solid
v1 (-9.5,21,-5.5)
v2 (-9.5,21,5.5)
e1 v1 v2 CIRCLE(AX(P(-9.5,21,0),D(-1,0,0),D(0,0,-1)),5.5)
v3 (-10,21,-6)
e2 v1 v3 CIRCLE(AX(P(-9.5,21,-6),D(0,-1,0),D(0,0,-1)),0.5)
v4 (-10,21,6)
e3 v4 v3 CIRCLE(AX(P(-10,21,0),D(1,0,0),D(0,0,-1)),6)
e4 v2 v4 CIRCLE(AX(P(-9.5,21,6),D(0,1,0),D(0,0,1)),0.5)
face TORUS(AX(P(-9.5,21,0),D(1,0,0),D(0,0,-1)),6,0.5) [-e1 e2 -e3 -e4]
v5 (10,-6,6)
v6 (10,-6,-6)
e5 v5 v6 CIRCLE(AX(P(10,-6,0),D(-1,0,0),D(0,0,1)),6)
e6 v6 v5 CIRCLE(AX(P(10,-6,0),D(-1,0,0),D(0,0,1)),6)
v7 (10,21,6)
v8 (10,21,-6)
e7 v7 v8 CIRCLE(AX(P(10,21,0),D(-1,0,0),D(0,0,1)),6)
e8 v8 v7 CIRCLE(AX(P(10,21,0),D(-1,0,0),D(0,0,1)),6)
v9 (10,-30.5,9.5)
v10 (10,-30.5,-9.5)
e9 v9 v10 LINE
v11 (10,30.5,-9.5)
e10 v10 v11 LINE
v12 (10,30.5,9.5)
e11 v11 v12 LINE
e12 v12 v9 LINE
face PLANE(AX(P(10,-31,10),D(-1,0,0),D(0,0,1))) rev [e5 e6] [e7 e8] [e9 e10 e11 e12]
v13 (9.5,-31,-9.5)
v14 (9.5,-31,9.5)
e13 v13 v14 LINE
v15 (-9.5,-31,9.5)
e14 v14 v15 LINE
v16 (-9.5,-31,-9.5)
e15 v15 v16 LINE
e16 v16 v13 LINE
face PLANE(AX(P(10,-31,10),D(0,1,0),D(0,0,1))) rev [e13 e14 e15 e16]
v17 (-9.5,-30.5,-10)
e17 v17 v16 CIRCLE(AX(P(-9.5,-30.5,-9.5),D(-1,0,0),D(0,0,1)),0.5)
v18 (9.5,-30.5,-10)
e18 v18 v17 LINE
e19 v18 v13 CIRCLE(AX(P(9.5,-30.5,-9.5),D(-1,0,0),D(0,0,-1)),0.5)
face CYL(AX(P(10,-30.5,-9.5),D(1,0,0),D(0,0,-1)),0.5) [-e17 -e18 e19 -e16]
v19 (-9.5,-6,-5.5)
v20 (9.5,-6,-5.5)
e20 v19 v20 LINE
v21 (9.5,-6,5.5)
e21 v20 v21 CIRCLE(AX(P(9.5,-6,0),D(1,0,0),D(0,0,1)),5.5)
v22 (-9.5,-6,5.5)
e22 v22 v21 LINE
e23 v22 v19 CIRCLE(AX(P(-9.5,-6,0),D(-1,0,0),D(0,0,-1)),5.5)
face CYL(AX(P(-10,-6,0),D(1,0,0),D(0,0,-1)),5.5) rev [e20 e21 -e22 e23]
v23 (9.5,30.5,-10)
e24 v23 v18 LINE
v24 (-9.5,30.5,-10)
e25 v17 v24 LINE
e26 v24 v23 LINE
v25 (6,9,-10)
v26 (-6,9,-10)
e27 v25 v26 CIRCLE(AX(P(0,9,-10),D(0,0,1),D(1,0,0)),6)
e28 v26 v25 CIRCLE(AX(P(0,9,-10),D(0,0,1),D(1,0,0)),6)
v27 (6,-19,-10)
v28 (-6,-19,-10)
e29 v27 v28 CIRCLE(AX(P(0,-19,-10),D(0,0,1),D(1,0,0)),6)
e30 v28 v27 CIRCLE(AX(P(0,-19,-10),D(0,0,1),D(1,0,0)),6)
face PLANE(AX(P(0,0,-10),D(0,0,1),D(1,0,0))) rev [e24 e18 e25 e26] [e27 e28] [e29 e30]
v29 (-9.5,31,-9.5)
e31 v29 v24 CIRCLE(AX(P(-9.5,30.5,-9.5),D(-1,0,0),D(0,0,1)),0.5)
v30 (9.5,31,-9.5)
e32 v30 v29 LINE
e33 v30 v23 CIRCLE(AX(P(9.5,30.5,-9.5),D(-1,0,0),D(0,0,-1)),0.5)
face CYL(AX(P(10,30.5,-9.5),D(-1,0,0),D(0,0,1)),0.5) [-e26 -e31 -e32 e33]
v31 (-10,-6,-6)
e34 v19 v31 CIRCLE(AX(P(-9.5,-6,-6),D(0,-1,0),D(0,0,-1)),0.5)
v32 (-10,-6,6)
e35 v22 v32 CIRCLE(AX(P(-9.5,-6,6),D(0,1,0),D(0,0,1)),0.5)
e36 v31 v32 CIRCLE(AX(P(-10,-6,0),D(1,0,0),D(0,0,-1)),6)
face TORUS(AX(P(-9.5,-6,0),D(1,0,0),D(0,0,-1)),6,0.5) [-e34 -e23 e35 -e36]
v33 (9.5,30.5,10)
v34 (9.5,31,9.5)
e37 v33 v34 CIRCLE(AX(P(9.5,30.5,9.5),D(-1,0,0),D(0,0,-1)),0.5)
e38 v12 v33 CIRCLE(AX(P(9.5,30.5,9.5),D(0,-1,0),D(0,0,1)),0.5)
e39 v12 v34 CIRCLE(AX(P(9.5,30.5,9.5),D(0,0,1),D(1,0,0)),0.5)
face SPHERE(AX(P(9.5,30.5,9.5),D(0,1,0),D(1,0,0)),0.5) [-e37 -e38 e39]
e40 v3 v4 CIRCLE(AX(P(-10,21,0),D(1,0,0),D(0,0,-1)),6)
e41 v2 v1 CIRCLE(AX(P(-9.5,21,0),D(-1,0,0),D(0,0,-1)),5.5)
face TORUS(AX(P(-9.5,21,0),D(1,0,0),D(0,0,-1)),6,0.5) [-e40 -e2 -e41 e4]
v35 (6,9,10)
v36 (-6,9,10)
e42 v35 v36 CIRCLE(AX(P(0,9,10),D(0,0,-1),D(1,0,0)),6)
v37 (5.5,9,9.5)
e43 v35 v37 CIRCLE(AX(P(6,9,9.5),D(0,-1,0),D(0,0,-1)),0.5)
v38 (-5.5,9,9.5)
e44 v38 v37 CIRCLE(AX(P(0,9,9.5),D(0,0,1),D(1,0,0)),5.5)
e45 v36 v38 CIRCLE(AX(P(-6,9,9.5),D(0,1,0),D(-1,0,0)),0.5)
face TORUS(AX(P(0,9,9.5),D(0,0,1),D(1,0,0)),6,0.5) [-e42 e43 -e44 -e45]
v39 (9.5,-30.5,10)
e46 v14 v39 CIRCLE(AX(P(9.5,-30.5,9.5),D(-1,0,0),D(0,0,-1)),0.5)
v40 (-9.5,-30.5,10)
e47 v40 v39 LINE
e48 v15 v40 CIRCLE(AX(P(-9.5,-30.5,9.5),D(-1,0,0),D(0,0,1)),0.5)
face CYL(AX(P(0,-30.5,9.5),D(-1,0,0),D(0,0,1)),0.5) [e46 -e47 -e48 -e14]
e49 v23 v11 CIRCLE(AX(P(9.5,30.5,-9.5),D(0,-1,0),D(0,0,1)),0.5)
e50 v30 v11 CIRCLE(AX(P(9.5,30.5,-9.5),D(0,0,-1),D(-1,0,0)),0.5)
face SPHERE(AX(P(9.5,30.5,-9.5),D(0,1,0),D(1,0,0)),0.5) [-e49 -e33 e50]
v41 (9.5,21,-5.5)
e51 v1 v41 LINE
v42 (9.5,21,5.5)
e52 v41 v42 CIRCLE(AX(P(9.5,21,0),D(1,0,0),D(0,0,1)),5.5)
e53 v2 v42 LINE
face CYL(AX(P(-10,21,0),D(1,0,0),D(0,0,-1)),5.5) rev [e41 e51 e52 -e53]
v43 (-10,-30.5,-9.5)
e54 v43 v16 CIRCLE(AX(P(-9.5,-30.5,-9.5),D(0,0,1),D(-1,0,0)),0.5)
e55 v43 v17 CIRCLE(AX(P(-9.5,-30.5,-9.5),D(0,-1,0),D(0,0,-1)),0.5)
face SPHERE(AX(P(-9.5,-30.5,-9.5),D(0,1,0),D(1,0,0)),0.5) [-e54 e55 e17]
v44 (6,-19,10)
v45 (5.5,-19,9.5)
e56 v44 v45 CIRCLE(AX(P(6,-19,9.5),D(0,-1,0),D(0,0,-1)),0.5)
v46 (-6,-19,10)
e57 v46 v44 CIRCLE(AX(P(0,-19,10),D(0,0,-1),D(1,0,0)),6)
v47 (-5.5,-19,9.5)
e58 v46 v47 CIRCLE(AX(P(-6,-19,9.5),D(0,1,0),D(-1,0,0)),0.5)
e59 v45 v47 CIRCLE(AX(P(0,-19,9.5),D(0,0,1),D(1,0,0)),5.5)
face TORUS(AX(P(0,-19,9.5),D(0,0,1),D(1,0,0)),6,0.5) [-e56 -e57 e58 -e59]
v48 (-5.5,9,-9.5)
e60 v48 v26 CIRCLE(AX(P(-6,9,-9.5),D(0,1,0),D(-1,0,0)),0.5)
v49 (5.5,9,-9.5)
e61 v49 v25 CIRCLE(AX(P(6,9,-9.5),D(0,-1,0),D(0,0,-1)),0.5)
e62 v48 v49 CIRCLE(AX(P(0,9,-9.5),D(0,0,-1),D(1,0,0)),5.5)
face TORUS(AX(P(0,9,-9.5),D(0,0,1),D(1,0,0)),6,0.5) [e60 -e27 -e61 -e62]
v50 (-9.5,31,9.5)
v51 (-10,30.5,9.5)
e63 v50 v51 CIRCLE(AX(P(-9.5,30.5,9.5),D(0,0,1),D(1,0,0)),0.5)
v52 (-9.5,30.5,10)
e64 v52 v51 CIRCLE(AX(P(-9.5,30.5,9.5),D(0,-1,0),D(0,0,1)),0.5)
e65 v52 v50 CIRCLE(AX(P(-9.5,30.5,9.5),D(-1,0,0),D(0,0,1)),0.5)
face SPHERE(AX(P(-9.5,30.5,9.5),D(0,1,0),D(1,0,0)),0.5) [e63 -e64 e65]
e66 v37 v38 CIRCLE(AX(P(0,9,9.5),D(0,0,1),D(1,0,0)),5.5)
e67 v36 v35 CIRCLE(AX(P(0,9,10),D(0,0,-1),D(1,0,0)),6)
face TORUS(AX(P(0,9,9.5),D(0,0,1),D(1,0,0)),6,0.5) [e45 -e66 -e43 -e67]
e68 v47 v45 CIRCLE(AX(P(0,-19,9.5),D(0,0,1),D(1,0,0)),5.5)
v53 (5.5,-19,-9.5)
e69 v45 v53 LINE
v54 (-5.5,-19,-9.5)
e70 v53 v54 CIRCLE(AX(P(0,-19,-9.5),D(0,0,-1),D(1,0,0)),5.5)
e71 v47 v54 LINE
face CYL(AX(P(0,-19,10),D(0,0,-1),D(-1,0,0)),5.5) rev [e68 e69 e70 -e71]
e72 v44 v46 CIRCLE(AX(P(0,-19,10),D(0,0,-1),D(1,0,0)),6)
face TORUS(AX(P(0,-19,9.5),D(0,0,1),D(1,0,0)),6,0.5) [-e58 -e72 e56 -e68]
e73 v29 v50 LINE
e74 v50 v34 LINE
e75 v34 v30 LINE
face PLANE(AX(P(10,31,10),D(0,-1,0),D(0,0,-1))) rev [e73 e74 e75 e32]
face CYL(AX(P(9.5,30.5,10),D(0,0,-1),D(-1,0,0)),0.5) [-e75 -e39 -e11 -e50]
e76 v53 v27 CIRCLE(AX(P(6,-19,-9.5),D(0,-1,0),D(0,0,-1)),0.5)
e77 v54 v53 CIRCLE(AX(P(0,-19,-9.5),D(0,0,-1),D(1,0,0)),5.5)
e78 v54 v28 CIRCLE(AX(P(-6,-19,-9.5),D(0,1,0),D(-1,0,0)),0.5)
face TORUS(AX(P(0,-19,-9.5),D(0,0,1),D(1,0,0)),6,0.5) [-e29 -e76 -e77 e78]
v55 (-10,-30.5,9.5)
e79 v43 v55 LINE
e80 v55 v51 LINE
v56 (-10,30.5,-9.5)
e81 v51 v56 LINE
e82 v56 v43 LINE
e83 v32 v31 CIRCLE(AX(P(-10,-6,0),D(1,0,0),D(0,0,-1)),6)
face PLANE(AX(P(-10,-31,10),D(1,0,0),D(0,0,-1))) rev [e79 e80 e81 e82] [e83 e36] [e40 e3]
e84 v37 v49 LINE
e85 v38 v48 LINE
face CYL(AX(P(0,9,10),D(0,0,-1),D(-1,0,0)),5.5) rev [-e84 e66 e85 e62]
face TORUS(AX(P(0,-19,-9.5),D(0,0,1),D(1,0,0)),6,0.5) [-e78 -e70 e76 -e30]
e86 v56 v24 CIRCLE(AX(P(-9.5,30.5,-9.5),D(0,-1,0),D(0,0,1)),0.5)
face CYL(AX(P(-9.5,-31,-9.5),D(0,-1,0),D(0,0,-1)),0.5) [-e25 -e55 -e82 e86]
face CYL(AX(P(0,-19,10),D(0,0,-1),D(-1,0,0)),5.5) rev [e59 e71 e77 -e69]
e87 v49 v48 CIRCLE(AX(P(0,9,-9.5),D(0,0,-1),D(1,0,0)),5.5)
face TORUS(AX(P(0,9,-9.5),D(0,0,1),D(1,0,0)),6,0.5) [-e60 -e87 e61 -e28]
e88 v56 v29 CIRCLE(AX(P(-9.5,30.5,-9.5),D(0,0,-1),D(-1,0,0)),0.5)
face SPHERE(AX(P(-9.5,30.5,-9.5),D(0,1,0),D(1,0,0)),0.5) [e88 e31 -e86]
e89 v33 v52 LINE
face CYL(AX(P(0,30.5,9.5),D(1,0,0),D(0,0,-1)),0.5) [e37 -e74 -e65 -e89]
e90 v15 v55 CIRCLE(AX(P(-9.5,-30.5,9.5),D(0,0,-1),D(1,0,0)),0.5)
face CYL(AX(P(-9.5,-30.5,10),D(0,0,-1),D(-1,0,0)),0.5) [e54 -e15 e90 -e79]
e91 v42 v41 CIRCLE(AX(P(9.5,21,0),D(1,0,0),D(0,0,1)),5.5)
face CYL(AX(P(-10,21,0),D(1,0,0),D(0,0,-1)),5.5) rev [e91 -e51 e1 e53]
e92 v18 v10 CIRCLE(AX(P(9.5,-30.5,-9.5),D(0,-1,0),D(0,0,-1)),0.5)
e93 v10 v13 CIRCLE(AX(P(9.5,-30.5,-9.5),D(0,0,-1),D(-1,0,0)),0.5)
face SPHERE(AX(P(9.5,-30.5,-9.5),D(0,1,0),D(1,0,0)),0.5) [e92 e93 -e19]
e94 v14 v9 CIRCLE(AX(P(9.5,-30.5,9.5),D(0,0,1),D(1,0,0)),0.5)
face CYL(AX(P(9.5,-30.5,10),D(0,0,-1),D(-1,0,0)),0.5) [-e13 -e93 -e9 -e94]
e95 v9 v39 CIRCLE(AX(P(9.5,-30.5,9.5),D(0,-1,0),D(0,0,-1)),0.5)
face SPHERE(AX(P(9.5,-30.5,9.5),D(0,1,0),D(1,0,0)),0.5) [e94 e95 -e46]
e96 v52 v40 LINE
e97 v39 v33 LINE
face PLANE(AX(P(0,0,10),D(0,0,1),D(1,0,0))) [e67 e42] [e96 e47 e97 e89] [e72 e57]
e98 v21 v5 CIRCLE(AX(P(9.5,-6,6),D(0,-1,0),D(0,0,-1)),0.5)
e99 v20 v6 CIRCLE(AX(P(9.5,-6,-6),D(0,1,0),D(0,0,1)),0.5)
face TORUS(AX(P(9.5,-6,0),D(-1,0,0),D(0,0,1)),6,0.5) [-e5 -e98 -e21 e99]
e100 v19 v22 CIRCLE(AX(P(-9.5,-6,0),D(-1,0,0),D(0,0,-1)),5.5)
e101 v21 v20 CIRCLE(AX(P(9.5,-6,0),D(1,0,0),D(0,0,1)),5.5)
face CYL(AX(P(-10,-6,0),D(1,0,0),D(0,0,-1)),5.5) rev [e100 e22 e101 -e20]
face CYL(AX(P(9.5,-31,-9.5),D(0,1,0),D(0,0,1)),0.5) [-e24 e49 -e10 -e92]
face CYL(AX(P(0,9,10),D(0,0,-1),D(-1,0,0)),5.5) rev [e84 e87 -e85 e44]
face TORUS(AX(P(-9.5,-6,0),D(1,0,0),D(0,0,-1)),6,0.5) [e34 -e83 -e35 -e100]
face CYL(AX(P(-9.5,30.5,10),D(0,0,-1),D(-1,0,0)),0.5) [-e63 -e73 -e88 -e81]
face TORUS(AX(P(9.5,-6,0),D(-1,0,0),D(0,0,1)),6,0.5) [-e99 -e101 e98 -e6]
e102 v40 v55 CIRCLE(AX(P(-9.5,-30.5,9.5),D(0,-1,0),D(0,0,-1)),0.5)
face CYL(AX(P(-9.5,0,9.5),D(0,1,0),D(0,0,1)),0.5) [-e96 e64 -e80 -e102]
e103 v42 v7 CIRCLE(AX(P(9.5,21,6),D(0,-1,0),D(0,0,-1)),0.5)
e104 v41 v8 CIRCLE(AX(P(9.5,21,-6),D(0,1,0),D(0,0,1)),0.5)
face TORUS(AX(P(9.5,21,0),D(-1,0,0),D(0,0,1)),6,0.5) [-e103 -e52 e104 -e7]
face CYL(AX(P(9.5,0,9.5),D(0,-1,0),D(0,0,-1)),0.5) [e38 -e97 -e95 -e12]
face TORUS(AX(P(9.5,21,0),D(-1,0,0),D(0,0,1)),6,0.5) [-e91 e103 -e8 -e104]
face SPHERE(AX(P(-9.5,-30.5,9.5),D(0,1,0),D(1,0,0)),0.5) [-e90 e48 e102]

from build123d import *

# Parameters (mm, degrees)
SKETCH1_W           = 20
SKETCH1_H           = 62
SKETCH1_R           = 5.5
BOSS_EXTRUDE1_DEPTH = 10
SKETCH2_R           = 5.5
CUT_EXTRUDE1_DEPTH  = 20
FILLET1_R           = 0.5


with BuildPart() as part:
    # Sketch1 → Boss-Extrude1 (new, symmetric)
    with BuildSketch(Plane.XY):
        Rectangle(SKETCH1_W, SKETCH1_H)
        with Locations((0, -19)):
            Circle(SKETCH1_R, mode=Mode.SUBTRACT)
        with Locations((0, 9)):
            Circle(SKETCH1_R, mode=Mode.SUBTRACT)
    extrude(amount=BOSS_EXTRUDE1_DEPTH, both=True)

    # Sketch2 → Cut-Extrude1 (cut)
    with BuildSketch(Plane(origin=(10, 0, 0), x_dir=(0, 0, -1), z_dir=(1, 0, 0))):
        with Locations((0, 21)):
            Circle(SKETCH2_R)
        with Locations((0, -6)):
            Circle(SKETCH2_R)
    extrude(amount=-CUT_EXTRUDE1_DEPTH, mode=Mode.SUBTRACT)

    # Fillet1
    fillet1_edges = [part.edges().sort_by_distance(p)[0] for p in [
        (10, 0, 10),
        (-5.5, -19, -10),
        (-5.5, -19, 10),
        (0, 31, 10),
        (-5.5, 9, -10),
        (-5.5, 9, 10),
        (-10, 21, 5.5),
        (10, 21, 5.5),
        (-10, -6, 5.5),
        (10, -6, 5.5),
        (-10, 0, 10),
        (0, 31, -10),
        (10, 0, -10),
        (0, -31, -10),
        (-10, 0, -10),
        (0, -31, 10),
        (-10, 31, 0),
        (10, 31, 0),
        (10, -31, 0),
        (-10, -31, 0),
    ]]
    fillet(fillet1_edges, radius=FILLET1_R)


solid = part.part
